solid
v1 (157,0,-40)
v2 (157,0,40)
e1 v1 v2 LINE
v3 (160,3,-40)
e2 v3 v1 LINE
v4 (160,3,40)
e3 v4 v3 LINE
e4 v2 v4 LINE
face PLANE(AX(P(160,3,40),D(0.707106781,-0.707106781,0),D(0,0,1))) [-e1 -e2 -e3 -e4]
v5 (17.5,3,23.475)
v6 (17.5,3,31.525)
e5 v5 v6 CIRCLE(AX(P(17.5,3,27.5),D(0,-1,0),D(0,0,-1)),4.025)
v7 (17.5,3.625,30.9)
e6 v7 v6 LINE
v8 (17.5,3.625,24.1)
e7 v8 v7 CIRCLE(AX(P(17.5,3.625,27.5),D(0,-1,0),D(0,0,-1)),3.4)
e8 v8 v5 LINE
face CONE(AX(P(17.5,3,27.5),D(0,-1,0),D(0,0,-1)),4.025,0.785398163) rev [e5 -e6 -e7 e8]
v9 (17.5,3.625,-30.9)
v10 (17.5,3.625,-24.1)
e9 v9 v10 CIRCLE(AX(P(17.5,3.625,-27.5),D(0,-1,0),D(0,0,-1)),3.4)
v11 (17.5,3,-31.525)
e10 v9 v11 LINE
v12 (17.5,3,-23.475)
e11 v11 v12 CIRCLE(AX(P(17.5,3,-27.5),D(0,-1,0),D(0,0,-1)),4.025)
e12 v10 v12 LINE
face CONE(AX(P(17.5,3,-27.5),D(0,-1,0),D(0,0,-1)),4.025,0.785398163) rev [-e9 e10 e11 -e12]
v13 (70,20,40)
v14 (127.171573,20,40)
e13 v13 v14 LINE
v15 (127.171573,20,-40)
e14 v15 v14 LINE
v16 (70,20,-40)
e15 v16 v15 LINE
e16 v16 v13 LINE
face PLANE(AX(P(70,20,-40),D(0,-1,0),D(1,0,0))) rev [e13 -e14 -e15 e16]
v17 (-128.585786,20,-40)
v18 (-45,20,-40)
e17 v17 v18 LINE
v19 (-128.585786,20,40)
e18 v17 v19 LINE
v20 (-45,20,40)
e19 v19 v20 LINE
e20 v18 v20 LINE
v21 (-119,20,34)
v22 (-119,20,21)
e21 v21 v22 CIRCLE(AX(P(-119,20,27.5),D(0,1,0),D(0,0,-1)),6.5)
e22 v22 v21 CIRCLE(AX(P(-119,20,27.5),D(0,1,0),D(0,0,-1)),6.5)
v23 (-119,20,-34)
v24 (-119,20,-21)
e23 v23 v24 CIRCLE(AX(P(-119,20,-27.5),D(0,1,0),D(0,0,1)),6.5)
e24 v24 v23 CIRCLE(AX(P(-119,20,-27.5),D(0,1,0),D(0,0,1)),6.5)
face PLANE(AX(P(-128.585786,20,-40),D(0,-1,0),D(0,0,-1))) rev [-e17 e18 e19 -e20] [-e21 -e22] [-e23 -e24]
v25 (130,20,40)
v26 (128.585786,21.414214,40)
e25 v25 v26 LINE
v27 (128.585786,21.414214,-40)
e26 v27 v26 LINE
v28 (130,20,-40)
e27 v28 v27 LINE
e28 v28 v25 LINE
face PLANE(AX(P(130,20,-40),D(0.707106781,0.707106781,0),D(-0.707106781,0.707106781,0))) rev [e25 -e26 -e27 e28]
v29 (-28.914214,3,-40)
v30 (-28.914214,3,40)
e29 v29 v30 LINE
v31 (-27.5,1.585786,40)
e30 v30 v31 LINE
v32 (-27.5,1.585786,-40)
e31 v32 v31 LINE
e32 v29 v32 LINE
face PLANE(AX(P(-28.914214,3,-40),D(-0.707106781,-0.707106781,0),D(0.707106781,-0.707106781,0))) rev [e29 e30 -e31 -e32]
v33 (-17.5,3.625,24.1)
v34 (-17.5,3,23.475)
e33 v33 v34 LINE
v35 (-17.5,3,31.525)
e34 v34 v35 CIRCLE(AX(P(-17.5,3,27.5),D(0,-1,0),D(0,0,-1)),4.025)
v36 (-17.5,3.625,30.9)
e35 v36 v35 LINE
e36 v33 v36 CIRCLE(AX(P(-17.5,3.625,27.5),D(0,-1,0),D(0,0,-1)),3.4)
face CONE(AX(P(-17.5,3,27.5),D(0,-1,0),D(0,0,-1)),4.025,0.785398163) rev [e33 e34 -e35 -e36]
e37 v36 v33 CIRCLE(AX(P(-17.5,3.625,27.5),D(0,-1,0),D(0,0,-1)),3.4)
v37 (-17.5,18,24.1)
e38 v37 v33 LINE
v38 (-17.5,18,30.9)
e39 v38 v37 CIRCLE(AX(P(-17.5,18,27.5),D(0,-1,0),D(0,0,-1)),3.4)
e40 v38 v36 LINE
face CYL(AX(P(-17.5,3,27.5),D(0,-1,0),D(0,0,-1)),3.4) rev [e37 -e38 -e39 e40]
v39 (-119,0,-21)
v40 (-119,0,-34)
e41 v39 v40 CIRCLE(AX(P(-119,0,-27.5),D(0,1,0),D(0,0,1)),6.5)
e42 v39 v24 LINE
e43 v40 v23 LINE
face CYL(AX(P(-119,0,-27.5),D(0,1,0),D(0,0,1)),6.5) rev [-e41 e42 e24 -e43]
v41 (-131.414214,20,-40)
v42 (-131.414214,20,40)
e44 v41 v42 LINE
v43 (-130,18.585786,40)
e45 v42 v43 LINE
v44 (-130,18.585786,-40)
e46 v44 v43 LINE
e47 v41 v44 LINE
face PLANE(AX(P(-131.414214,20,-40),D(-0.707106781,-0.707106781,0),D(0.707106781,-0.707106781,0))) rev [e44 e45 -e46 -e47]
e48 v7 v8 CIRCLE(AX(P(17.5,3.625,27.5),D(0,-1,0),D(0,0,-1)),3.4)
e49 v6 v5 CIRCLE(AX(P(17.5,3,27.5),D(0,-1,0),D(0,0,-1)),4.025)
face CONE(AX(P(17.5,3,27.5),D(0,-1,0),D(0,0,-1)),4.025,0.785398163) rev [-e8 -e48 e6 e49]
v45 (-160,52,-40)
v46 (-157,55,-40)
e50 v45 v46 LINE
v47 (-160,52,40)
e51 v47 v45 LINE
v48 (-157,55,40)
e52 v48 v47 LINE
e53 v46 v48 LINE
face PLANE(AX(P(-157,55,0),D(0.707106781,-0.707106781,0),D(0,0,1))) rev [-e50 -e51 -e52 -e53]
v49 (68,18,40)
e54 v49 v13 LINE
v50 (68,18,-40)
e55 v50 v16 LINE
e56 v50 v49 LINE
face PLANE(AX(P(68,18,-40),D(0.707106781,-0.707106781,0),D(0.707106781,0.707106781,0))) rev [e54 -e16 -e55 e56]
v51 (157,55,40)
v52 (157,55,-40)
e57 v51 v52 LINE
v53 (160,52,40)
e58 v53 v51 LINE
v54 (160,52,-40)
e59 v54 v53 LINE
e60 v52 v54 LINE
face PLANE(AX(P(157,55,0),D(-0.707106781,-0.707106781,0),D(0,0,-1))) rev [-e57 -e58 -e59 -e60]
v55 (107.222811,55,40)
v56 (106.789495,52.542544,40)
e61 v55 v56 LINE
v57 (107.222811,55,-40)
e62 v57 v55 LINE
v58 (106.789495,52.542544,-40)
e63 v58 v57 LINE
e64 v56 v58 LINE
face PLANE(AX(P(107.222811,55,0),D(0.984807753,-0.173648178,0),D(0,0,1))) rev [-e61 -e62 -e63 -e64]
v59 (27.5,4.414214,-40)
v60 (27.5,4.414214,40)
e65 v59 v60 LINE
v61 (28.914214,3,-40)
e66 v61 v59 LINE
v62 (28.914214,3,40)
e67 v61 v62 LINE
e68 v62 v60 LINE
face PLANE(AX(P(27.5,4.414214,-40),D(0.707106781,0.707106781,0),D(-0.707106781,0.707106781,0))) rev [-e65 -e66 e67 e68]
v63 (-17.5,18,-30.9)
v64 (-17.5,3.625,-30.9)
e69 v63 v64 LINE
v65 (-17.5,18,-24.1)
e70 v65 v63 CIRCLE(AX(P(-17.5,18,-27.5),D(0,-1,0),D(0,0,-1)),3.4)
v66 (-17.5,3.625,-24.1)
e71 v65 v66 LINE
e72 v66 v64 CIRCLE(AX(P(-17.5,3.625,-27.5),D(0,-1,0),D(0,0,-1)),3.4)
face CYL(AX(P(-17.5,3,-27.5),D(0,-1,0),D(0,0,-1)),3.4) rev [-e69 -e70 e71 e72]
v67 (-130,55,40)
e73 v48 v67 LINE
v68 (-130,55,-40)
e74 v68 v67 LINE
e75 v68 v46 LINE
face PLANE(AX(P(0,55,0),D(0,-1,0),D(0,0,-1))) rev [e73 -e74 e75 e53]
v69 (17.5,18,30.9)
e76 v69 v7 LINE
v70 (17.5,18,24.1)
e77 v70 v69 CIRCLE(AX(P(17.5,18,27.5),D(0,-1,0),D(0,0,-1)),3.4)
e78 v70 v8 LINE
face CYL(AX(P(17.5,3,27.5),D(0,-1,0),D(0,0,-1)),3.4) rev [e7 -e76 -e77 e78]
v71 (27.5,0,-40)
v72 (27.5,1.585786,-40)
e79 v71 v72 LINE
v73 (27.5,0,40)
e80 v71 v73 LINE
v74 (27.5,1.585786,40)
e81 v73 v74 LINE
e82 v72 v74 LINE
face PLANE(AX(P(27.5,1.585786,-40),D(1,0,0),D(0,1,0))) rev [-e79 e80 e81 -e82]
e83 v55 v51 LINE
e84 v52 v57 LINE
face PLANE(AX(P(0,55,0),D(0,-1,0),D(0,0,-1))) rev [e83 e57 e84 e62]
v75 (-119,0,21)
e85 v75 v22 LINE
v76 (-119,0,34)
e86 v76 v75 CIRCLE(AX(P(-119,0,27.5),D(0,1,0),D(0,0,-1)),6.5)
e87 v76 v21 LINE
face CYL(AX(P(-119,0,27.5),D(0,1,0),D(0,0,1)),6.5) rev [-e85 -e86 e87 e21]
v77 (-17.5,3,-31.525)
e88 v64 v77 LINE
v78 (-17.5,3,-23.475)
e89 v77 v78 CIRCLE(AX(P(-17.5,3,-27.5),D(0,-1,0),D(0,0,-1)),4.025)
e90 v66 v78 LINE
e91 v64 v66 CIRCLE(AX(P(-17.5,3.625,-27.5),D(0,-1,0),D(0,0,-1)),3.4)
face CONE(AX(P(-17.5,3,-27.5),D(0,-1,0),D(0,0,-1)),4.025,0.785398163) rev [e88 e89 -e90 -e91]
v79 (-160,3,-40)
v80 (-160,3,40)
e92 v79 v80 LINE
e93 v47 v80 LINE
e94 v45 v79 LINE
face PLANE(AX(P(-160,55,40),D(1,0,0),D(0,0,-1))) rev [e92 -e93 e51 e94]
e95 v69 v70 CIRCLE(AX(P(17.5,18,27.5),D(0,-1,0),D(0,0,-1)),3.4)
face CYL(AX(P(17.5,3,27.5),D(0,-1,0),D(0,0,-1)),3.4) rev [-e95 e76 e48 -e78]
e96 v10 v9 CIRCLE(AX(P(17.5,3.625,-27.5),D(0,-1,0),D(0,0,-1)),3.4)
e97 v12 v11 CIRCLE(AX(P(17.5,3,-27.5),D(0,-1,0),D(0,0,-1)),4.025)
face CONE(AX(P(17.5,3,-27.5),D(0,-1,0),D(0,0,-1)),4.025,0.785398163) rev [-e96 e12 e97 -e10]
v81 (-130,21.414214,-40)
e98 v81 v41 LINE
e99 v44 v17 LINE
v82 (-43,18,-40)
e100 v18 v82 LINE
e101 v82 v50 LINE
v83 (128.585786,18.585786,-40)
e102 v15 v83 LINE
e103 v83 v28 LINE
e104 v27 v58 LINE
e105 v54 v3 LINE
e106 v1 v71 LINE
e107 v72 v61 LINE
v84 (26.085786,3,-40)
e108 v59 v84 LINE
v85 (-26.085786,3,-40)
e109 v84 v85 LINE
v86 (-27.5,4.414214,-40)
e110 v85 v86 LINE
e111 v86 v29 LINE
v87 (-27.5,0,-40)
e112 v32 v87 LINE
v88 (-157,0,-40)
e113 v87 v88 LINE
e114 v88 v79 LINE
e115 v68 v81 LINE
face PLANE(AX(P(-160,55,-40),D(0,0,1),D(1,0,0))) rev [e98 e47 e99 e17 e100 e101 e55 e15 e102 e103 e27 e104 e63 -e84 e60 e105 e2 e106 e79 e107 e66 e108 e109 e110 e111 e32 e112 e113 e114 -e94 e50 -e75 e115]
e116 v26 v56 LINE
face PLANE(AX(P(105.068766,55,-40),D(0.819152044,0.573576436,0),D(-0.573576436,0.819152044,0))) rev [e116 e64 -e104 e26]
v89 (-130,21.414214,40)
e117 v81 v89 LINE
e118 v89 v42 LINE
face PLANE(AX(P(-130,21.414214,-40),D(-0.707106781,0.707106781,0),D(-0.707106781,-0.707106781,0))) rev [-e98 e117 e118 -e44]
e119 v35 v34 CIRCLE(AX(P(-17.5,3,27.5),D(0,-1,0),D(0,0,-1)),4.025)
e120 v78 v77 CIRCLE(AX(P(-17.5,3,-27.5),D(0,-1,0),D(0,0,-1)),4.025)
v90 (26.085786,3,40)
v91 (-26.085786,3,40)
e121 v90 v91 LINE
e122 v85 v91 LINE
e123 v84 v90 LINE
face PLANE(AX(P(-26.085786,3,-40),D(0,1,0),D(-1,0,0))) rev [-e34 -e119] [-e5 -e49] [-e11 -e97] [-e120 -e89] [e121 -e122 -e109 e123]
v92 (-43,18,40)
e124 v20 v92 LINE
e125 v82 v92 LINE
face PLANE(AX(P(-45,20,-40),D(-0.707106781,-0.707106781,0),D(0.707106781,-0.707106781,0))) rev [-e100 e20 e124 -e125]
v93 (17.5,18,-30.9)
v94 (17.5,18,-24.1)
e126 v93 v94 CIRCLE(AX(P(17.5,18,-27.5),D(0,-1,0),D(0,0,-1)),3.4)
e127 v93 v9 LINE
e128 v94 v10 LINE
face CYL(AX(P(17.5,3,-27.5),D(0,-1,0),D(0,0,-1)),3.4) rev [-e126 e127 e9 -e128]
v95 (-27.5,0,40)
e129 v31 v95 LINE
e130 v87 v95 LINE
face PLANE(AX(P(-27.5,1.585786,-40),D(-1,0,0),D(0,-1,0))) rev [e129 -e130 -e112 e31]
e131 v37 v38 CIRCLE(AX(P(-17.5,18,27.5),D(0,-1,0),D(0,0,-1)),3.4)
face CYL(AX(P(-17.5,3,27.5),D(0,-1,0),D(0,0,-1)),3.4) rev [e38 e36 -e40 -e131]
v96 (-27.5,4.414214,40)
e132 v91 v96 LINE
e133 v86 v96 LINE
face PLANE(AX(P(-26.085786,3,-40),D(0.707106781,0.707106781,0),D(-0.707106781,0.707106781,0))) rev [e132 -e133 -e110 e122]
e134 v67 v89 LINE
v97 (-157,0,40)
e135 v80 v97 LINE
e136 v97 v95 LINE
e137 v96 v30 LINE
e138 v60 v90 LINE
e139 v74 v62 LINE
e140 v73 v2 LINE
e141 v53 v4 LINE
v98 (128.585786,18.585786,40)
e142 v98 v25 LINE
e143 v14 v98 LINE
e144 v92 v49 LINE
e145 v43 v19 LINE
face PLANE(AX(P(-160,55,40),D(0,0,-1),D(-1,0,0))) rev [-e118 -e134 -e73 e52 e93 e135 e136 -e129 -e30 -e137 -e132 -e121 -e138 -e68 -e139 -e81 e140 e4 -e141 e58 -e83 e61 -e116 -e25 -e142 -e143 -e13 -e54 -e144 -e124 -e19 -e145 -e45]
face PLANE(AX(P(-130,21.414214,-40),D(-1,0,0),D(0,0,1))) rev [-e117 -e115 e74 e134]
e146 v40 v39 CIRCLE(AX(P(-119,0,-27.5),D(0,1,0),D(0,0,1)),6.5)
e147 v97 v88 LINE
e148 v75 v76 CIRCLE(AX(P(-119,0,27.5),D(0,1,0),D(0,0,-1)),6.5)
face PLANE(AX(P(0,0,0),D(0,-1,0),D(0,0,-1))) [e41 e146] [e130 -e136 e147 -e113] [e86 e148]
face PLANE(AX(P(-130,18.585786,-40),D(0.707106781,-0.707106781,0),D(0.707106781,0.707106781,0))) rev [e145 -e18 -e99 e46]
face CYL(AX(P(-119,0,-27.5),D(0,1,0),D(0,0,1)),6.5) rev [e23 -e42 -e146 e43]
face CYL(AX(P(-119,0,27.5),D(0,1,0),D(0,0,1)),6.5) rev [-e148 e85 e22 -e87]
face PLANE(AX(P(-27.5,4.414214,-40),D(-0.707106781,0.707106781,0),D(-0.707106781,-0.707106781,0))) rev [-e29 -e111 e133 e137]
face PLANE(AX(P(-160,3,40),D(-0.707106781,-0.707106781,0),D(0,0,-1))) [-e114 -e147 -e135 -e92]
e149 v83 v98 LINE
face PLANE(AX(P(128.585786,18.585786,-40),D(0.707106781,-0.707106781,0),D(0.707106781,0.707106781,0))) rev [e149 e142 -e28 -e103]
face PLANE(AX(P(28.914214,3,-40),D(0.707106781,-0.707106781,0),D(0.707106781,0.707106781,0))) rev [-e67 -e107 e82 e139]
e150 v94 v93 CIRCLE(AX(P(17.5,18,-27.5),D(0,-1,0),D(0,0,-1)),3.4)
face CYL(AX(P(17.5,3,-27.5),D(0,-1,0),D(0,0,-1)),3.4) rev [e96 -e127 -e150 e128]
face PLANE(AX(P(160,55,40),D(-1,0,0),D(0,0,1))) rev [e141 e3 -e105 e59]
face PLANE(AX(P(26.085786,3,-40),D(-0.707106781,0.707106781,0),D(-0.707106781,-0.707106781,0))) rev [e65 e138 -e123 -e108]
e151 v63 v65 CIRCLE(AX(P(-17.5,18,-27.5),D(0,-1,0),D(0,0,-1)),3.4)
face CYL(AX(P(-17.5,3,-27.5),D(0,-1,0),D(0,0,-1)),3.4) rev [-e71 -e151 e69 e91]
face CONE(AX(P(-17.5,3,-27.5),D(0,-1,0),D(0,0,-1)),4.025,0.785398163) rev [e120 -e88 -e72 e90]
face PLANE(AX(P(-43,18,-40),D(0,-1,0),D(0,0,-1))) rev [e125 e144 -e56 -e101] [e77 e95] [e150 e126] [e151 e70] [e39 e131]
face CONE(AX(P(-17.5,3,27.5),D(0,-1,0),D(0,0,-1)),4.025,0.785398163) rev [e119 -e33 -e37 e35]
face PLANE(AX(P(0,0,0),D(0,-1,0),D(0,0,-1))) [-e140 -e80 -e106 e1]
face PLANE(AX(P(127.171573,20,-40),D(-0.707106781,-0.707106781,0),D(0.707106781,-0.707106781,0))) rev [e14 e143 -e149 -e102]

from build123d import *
from OCP.BRepFilletAPI import BRepFilletAPI_MakeChamfer

# Parameters (mm, degrees)
SKETCH1_W           = 320
SKETCH1_H           = 80
BOSS_EXTRUDE1_DEPTH = 55
CUT_EXTRUDE1_DEPTH  = 188.149672722
CUT_EXTRUDE2_DEPTH  = 188.149672722
SKETCH7_R           = 6.5
CUT_EXTRUDE3_DEPTH  = 169.597153001
CHAMFER1_SIZE       = 3
CHAMFER1_SIZE2      = 2.154045129


with BuildPart() as part:
    # Sketch1 → Boss-Extrude1 (new body)
    with BuildSketch(Plane(origin=(0, 0, 0), x_dir=(1, 0, 0), z_dir=(0, 1, 0))):
        Rectangle(SKETCH1_W, SKETCH1_H)
    extrude(amount=BOSS_EXTRUDE1_DEPTH)

    # Sketch2 → Cut-Extrude1 (cut, through all)
    with BuildSketch(Plane.XY.offset(40)):
        Polygon((105.068765597, 55), (128.585786438, 21.414213562), (130, 20), (128.585786438, 18.585786438), (127.171572875, 20), (70, 20), (68, 18), (-43, 18), (-45, 20), (-128.585786438, 20), (-130, 18.585786438), (-131.414213562, 20), (-130, 21.414213562), (-130, 55), align=None)
    extrude(amount=-CUT_EXTRUDE1_DEPTH, mode=Mode.SUBTRACT)

    # Sketch3 → Cut-Extrude2 (cut, through all)
    with BuildSketch(Plane.XY.offset(40)):
        Polygon((-26.085786438, 3), (26.085786438, 3), (27.5, 4.414213562), (28.914213562, 3), (27.5, 1.585786438), (27.5, 0), (-27.5, 0), (-27.5, 1.585786438), (-28.914213562, 3), (-27.5, 4.414213562), align=None)
    extrude(amount=-CUT_EXTRUDE2_DEPTH, mode=Mode.SUBTRACT)

    # Sketch6 → M8 Tapped Hole1 (revolve, cut)
    with BuildSketch(Plane(origin=(17.5, 3, -27.5), x_dir=(0, 0, -1), z_dir=(1, 0, 0))):
        Polygon((0, 0), (0, 21.792926105), (3.4, 19.75), (3.4, 0.625), (4.025, 0), align=None)
    m8_tapped_hole1 = revolve(axis=Axis((17.5, -3.35, -27.5), (0, 1, 0)), mode=Mode.SUBTRACT)

    # Mirror1: M8 Tapped Hole1 across plane
    add(m8_tapped_hole1.mirror(Plane(origin=(0, 0, 0), x_dir=(0, 0, 1), z_dir=(1, 0, 0))), mode=Mode.SUBTRACT)

    # Mirror2: M8 Tapped Hole1 across plane
    add(m8_tapped_hole1.mirror(Plane.XY), mode=Mode.SUBTRACT)

    # Mirror2 copy 1 sketch → Mirror2 copy 1 (revolve, cut)
    with BuildSketch(Plane(origin=(-17.5, 3, 27.5), x_dir=(0, 0, 1), z_dir=(-1, 0, 0))):
        Polygon((0, 0), (0, 21.792926105), (3.4, 19.75), (3.4, 0.625), (4.025, 0), align=None)
    revolve(axis=Axis((-17.5, -3.35, 27.5), (0, 1, 0)), mode=Mode.SUBTRACT)

    # Sketch7 → Cut-Extrude3 (cut, through all)
    with BuildSketch(Plane(origin=(0, 20, 0), x_dir=(1, 0, 0), z_dir=(0, 1, 0))):
        with Locations(Location((-119, 27.5, 0), (0, 0, 270))):
            Circle(SKETCH7_R)
        with Locations(Location((-119, -27.5, 0), (0, 0, 90))):
            Circle(SKETCH7_R)
    extrude(amount=-CUT_EXTRUDE3_DEPTH, mode=Mode.SUBTRACT)

    # Chamfer1: one chamfer whose edges measure the first distance from different faces: ONE call of the kernel's chamfer builder (chamfer() names one face for all edges)
    chamfer1_edges_1 = [part.edges().sort_by_distance(p)[0] for p in [
        (-160, 55, 0),
        (160, 55, 0),
        (-160, 0, 0),
        (160, 0, 0),
    ]]
    chamfer1_edges_2 = [part.edges().sort_by_distance(p)[0] for p in [
        (105.068765597, 55, 0),
    ]]
    chamfer1_side_2 = [part.faces().sort_by_distance(p)[0] for p in [
        (116.827276017, 38.207106781, 0),
    ]]
    chamfer1 = BRepFilletAPI_MakeChamfer(part.part.solid().wrapped)
    for e in chamfer1_edges_1:
        chamfer1.Add(CHAMFER1_SIZE, e.wrapped)
    for e in chamfer1_edges_2:
        chamfer1.Add(CHAMFER1_SIZE, CHAMFER1_SIZE2, e.wrapped, chamfer1_side_2[0].wrapped)  # the first distance lies on this face
    add(Compound.cast(chamfer1.Shape()), mode=Mode.REPLACE)


solid = part.part
